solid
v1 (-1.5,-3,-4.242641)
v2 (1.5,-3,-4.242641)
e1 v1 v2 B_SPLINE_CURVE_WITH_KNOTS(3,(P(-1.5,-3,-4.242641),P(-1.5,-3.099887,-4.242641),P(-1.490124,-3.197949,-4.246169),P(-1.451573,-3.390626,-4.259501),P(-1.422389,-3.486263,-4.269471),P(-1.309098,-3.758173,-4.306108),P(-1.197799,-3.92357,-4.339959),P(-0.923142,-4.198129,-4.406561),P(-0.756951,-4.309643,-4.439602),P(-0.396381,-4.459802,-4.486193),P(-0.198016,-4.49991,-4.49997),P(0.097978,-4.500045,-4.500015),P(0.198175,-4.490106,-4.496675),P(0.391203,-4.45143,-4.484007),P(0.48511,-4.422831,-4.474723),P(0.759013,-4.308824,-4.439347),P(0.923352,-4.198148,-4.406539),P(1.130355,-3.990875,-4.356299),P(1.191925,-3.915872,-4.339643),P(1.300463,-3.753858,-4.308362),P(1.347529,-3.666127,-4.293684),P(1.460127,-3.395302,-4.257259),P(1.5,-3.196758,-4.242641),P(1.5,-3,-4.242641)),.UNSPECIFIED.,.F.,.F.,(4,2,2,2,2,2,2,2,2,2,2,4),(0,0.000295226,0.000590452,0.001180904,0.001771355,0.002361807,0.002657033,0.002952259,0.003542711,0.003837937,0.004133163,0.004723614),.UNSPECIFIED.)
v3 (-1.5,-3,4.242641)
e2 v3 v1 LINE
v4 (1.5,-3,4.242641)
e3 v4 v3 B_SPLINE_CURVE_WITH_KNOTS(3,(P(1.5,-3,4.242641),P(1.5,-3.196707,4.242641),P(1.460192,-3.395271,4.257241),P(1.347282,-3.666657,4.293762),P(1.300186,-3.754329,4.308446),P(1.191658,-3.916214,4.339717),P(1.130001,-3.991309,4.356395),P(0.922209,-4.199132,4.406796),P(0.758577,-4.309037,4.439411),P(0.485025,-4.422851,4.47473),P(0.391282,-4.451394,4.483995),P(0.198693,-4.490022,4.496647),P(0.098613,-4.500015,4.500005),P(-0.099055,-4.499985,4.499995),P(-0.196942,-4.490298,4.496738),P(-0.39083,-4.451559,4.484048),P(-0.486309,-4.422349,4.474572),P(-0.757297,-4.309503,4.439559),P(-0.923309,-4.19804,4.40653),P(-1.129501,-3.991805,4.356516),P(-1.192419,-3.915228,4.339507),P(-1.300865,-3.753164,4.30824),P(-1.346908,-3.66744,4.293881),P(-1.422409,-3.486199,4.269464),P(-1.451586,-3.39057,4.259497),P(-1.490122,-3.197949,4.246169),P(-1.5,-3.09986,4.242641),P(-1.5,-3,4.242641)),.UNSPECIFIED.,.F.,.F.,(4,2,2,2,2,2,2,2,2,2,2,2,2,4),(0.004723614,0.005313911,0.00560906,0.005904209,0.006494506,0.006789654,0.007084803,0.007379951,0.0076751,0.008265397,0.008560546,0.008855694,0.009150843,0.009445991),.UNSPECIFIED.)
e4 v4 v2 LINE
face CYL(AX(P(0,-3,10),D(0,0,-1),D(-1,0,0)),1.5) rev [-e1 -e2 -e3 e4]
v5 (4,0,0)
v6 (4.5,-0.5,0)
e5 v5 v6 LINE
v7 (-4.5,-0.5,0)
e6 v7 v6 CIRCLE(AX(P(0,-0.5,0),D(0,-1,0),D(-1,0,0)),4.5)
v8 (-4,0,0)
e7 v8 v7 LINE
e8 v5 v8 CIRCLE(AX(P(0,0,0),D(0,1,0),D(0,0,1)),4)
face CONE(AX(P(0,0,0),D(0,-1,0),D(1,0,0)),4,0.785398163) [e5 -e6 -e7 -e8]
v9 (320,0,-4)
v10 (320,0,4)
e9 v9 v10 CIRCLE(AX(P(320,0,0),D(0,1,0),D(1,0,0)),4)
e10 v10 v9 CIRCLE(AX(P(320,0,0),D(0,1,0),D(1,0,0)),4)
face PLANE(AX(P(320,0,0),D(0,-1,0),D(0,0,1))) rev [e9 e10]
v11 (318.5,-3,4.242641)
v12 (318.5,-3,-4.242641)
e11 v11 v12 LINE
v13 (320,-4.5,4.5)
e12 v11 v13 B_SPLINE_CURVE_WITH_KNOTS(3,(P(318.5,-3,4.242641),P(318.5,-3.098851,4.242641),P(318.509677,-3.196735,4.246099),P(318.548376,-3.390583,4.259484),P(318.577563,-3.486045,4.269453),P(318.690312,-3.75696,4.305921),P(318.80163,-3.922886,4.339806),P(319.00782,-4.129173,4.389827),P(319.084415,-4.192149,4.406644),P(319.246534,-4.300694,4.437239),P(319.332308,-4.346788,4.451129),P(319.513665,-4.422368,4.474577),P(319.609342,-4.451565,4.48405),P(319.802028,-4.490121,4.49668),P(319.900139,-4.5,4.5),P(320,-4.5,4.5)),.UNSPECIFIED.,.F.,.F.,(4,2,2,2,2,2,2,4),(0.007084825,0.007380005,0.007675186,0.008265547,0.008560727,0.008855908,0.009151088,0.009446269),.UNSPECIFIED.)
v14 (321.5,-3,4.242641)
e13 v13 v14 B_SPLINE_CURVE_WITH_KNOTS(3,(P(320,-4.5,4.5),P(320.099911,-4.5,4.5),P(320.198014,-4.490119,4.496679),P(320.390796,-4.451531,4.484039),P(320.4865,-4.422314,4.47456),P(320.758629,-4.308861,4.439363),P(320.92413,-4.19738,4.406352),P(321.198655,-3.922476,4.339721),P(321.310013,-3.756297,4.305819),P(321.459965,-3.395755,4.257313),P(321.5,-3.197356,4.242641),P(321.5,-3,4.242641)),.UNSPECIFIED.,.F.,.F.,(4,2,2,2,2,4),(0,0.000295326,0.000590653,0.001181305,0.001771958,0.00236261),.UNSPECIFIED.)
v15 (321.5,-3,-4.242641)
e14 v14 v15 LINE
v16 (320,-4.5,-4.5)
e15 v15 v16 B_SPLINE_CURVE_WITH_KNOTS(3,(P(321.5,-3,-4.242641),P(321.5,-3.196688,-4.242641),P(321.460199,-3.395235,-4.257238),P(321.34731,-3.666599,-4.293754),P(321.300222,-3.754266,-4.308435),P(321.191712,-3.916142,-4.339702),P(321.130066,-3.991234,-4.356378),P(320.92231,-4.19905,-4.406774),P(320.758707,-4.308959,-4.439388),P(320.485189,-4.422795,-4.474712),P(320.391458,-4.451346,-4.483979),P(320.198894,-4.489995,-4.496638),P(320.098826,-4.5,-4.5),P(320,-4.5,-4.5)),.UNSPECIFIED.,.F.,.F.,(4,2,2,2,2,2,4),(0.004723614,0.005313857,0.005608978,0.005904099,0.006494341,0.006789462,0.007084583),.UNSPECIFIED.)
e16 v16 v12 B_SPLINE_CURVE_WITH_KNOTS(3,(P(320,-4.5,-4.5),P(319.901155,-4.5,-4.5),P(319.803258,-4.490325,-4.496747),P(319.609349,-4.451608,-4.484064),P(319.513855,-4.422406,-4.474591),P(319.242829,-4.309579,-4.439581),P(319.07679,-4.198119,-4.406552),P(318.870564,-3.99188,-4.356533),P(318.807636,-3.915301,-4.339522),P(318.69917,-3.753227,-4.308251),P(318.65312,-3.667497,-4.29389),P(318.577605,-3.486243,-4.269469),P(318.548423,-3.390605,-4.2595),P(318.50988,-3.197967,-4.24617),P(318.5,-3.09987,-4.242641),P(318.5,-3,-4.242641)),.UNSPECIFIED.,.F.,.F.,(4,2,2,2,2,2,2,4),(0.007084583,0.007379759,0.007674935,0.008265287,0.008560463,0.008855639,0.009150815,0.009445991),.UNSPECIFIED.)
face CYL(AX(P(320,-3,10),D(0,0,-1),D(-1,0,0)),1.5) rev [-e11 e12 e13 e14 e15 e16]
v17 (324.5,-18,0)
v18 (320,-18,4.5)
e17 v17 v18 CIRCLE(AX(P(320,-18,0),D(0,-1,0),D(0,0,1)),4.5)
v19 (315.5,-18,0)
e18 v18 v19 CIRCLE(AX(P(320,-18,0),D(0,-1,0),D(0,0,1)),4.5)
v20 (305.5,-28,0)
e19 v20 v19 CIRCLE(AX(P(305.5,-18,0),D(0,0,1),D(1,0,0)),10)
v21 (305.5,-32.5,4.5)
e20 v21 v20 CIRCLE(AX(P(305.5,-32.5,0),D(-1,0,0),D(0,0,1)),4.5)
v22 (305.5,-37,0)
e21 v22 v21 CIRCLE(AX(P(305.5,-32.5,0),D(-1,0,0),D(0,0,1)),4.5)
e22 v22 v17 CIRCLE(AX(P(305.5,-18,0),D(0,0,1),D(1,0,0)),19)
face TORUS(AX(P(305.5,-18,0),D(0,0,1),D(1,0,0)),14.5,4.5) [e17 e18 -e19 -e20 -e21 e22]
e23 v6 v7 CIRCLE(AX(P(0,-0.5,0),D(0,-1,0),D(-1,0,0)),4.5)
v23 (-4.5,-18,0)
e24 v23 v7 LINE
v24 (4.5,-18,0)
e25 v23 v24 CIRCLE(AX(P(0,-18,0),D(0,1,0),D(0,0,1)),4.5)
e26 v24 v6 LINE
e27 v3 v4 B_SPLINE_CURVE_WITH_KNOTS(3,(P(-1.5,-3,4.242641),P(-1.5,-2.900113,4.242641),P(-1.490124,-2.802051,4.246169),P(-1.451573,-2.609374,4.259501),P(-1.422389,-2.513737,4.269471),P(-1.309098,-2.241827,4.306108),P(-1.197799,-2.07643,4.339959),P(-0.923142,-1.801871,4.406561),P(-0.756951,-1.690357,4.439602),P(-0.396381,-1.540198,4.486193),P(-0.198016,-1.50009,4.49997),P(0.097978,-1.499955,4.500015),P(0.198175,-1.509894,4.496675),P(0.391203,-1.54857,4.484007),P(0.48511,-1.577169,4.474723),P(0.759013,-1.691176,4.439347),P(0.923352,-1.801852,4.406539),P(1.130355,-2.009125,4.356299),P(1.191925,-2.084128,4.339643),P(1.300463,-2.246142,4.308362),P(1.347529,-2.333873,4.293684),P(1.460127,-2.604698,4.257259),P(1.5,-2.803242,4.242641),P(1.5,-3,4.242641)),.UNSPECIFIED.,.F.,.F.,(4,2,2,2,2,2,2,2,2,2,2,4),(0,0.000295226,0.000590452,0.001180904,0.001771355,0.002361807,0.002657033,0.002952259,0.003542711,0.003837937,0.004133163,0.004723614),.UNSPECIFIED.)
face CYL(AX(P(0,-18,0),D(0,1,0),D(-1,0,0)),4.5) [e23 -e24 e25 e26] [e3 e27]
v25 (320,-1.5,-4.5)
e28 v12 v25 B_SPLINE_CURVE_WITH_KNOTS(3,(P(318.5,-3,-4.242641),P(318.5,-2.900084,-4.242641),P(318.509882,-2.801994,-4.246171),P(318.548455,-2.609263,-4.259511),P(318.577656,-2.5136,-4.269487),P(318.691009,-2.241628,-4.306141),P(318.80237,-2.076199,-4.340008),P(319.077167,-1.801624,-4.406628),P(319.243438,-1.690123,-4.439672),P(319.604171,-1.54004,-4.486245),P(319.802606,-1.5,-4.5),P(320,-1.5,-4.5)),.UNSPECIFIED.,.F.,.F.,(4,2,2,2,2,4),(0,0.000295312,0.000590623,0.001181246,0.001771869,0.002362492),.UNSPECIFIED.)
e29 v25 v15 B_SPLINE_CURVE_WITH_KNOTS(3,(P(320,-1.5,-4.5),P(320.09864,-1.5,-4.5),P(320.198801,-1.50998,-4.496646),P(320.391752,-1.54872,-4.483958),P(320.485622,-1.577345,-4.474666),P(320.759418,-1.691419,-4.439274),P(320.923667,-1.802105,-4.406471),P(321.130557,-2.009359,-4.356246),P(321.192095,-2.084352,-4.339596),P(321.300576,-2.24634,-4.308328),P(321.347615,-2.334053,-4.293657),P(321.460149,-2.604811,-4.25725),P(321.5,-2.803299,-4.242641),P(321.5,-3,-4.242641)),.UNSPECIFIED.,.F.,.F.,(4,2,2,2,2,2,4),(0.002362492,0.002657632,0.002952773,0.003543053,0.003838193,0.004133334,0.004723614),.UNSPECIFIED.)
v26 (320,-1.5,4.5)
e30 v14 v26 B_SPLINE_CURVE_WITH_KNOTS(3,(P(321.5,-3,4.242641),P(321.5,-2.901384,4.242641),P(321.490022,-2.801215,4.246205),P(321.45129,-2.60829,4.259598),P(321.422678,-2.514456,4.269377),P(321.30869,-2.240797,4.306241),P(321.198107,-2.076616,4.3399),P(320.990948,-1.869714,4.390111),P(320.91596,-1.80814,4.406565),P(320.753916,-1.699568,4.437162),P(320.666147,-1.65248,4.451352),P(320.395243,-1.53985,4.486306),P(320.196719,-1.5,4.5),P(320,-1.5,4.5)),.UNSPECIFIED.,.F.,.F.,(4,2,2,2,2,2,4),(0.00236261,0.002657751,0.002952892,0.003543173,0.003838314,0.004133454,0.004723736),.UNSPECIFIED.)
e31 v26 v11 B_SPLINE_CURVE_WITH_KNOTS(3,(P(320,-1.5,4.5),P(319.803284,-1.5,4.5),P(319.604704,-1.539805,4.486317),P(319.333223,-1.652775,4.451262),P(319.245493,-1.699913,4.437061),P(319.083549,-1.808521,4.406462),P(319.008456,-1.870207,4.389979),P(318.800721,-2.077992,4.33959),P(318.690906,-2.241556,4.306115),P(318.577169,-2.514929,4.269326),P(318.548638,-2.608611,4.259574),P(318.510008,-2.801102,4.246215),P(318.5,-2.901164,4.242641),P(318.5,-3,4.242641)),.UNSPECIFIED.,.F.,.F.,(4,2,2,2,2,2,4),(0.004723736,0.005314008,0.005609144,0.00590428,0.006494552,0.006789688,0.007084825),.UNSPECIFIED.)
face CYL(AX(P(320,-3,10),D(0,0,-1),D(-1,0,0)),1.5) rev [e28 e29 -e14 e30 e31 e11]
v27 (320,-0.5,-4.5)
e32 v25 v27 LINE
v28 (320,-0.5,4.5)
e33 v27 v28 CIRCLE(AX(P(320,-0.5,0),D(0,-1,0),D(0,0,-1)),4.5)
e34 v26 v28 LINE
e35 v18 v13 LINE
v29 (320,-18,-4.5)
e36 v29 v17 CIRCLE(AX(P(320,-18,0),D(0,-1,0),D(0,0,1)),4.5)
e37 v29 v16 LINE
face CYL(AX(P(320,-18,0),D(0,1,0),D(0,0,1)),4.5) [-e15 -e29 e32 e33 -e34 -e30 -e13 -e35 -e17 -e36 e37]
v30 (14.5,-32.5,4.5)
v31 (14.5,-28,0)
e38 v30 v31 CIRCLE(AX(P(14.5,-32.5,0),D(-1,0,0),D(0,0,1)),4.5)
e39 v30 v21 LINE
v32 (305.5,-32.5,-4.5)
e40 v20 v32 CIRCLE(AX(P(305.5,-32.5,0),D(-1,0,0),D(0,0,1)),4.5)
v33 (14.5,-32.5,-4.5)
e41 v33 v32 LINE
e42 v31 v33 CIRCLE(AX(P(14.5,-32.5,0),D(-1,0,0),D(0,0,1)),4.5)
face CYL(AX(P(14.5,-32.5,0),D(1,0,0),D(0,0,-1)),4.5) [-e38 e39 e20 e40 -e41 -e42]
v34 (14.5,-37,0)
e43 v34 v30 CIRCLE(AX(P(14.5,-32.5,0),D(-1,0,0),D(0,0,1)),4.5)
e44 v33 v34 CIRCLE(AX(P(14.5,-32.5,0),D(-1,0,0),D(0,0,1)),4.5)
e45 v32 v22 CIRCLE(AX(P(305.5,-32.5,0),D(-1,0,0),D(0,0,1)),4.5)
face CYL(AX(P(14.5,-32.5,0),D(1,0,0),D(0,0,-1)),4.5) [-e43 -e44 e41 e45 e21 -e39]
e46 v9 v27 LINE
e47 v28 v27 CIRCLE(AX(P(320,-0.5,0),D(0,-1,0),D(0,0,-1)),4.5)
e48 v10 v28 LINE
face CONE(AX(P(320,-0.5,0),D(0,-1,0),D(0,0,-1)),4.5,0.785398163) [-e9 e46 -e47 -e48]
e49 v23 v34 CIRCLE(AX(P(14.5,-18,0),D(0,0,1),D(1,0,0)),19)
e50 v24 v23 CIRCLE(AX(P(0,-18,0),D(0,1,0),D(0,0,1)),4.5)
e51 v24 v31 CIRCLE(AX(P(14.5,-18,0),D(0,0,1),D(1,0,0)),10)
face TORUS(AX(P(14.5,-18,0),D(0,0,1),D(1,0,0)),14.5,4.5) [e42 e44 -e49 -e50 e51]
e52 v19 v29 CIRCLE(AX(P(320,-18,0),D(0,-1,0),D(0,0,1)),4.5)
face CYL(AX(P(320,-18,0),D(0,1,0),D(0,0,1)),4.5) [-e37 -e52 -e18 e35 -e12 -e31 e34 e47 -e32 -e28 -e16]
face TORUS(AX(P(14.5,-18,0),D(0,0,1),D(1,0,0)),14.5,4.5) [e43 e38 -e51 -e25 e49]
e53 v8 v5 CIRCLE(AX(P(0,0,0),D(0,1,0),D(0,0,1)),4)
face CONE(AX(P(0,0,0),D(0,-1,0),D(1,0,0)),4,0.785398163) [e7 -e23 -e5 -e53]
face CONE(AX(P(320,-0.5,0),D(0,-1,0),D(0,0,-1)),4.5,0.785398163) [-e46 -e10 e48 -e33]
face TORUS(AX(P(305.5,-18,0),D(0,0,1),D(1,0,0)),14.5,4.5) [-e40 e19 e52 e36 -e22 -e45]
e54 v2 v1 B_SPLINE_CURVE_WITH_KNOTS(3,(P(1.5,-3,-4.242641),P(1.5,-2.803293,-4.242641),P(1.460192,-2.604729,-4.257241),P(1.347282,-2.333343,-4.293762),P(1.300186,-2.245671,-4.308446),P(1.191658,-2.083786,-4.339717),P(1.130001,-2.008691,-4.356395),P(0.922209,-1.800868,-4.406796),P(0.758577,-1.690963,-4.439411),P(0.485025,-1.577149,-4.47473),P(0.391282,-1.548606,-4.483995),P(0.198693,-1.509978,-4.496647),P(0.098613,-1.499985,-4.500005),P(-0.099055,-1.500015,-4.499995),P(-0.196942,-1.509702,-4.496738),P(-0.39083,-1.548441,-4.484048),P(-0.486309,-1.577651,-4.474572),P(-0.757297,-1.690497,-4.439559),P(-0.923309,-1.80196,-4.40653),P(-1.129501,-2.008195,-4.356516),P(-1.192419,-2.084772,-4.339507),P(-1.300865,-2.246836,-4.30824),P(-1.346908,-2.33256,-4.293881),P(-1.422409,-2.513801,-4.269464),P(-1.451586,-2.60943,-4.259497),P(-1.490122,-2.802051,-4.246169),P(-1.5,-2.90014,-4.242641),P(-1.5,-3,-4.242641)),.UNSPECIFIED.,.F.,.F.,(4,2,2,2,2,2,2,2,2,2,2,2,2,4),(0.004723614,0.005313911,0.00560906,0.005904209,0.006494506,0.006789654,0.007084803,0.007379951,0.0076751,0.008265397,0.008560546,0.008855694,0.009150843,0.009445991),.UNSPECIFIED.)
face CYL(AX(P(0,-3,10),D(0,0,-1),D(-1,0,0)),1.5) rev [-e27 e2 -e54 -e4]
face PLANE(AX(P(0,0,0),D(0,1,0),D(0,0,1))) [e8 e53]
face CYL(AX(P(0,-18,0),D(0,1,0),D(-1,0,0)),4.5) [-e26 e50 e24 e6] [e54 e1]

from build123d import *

# Parameters (mm, degrees)
SKETCH2_R               = 4.5
CUT_EXTRUDE1_DEPTH      = 10
CUT_EXTRUDE1_DEPTH_BACK = 10
SKETCH3_R               = 1.5
CHAMFER1_SIZE           = 0.5


with BuildPart() as part:
    # Sweep1: sweep along a path in Sketch1
    with BuildLine(Plane.XY) as sweep1_path:
        Line((0, 0), (0, -18))
        ThreePointArc((0, -18), (4.246951673, -28.253048327), (14.5, -32.5))
        Line((14.5, -32.5), (305.5, -32.5))
        ThreePointArc((305.5, -32.5), (315.753048327, -28.253048327), (320, -18))
        Line((320, -18), (320, 0))
    # Sketch2 → Sweep1 (sweep)
    with BuildSketch(Plane(origin=(0, 0, 0), x_dir=(1, 0, 0), z_dir=(0, 1, 0))):
        Circle(SKETCH2_R)
    sweep(path=sweep1_path.line)

    # Sketch3 → Cut-Extrude1 (cut, two sides: drawn at the far end of the back side and taken through both)
    with BuildSketch(Plane.XY.offset(-CUT_EXTRUDE1_DEPTH_BACK)):
        with Locations(Location((320, -3, 0), (0, 0, 180))):
            Circle(SKETCH3_R)
        with Locations(Location((0, -3, 0), (0, 0, 180))):
            Circle(SKETCH3_R)
    extrude(amount=CUT_EXTRUDE1_DEPTH + CUT_EXTRUDE1_DEPTH_BACK, mode=Mode.SUBTRACT)

    # Chamfer1
    chamfer1_edges = [part.edges().sort_by_distance(p)[0] for p in [
        (-4.5, 0, 0),
        (324.5, 0, 0),
    ]]
    chamfer(chamfer1_edges, length=CHAMFER1_SIZE)


solid = part.part
